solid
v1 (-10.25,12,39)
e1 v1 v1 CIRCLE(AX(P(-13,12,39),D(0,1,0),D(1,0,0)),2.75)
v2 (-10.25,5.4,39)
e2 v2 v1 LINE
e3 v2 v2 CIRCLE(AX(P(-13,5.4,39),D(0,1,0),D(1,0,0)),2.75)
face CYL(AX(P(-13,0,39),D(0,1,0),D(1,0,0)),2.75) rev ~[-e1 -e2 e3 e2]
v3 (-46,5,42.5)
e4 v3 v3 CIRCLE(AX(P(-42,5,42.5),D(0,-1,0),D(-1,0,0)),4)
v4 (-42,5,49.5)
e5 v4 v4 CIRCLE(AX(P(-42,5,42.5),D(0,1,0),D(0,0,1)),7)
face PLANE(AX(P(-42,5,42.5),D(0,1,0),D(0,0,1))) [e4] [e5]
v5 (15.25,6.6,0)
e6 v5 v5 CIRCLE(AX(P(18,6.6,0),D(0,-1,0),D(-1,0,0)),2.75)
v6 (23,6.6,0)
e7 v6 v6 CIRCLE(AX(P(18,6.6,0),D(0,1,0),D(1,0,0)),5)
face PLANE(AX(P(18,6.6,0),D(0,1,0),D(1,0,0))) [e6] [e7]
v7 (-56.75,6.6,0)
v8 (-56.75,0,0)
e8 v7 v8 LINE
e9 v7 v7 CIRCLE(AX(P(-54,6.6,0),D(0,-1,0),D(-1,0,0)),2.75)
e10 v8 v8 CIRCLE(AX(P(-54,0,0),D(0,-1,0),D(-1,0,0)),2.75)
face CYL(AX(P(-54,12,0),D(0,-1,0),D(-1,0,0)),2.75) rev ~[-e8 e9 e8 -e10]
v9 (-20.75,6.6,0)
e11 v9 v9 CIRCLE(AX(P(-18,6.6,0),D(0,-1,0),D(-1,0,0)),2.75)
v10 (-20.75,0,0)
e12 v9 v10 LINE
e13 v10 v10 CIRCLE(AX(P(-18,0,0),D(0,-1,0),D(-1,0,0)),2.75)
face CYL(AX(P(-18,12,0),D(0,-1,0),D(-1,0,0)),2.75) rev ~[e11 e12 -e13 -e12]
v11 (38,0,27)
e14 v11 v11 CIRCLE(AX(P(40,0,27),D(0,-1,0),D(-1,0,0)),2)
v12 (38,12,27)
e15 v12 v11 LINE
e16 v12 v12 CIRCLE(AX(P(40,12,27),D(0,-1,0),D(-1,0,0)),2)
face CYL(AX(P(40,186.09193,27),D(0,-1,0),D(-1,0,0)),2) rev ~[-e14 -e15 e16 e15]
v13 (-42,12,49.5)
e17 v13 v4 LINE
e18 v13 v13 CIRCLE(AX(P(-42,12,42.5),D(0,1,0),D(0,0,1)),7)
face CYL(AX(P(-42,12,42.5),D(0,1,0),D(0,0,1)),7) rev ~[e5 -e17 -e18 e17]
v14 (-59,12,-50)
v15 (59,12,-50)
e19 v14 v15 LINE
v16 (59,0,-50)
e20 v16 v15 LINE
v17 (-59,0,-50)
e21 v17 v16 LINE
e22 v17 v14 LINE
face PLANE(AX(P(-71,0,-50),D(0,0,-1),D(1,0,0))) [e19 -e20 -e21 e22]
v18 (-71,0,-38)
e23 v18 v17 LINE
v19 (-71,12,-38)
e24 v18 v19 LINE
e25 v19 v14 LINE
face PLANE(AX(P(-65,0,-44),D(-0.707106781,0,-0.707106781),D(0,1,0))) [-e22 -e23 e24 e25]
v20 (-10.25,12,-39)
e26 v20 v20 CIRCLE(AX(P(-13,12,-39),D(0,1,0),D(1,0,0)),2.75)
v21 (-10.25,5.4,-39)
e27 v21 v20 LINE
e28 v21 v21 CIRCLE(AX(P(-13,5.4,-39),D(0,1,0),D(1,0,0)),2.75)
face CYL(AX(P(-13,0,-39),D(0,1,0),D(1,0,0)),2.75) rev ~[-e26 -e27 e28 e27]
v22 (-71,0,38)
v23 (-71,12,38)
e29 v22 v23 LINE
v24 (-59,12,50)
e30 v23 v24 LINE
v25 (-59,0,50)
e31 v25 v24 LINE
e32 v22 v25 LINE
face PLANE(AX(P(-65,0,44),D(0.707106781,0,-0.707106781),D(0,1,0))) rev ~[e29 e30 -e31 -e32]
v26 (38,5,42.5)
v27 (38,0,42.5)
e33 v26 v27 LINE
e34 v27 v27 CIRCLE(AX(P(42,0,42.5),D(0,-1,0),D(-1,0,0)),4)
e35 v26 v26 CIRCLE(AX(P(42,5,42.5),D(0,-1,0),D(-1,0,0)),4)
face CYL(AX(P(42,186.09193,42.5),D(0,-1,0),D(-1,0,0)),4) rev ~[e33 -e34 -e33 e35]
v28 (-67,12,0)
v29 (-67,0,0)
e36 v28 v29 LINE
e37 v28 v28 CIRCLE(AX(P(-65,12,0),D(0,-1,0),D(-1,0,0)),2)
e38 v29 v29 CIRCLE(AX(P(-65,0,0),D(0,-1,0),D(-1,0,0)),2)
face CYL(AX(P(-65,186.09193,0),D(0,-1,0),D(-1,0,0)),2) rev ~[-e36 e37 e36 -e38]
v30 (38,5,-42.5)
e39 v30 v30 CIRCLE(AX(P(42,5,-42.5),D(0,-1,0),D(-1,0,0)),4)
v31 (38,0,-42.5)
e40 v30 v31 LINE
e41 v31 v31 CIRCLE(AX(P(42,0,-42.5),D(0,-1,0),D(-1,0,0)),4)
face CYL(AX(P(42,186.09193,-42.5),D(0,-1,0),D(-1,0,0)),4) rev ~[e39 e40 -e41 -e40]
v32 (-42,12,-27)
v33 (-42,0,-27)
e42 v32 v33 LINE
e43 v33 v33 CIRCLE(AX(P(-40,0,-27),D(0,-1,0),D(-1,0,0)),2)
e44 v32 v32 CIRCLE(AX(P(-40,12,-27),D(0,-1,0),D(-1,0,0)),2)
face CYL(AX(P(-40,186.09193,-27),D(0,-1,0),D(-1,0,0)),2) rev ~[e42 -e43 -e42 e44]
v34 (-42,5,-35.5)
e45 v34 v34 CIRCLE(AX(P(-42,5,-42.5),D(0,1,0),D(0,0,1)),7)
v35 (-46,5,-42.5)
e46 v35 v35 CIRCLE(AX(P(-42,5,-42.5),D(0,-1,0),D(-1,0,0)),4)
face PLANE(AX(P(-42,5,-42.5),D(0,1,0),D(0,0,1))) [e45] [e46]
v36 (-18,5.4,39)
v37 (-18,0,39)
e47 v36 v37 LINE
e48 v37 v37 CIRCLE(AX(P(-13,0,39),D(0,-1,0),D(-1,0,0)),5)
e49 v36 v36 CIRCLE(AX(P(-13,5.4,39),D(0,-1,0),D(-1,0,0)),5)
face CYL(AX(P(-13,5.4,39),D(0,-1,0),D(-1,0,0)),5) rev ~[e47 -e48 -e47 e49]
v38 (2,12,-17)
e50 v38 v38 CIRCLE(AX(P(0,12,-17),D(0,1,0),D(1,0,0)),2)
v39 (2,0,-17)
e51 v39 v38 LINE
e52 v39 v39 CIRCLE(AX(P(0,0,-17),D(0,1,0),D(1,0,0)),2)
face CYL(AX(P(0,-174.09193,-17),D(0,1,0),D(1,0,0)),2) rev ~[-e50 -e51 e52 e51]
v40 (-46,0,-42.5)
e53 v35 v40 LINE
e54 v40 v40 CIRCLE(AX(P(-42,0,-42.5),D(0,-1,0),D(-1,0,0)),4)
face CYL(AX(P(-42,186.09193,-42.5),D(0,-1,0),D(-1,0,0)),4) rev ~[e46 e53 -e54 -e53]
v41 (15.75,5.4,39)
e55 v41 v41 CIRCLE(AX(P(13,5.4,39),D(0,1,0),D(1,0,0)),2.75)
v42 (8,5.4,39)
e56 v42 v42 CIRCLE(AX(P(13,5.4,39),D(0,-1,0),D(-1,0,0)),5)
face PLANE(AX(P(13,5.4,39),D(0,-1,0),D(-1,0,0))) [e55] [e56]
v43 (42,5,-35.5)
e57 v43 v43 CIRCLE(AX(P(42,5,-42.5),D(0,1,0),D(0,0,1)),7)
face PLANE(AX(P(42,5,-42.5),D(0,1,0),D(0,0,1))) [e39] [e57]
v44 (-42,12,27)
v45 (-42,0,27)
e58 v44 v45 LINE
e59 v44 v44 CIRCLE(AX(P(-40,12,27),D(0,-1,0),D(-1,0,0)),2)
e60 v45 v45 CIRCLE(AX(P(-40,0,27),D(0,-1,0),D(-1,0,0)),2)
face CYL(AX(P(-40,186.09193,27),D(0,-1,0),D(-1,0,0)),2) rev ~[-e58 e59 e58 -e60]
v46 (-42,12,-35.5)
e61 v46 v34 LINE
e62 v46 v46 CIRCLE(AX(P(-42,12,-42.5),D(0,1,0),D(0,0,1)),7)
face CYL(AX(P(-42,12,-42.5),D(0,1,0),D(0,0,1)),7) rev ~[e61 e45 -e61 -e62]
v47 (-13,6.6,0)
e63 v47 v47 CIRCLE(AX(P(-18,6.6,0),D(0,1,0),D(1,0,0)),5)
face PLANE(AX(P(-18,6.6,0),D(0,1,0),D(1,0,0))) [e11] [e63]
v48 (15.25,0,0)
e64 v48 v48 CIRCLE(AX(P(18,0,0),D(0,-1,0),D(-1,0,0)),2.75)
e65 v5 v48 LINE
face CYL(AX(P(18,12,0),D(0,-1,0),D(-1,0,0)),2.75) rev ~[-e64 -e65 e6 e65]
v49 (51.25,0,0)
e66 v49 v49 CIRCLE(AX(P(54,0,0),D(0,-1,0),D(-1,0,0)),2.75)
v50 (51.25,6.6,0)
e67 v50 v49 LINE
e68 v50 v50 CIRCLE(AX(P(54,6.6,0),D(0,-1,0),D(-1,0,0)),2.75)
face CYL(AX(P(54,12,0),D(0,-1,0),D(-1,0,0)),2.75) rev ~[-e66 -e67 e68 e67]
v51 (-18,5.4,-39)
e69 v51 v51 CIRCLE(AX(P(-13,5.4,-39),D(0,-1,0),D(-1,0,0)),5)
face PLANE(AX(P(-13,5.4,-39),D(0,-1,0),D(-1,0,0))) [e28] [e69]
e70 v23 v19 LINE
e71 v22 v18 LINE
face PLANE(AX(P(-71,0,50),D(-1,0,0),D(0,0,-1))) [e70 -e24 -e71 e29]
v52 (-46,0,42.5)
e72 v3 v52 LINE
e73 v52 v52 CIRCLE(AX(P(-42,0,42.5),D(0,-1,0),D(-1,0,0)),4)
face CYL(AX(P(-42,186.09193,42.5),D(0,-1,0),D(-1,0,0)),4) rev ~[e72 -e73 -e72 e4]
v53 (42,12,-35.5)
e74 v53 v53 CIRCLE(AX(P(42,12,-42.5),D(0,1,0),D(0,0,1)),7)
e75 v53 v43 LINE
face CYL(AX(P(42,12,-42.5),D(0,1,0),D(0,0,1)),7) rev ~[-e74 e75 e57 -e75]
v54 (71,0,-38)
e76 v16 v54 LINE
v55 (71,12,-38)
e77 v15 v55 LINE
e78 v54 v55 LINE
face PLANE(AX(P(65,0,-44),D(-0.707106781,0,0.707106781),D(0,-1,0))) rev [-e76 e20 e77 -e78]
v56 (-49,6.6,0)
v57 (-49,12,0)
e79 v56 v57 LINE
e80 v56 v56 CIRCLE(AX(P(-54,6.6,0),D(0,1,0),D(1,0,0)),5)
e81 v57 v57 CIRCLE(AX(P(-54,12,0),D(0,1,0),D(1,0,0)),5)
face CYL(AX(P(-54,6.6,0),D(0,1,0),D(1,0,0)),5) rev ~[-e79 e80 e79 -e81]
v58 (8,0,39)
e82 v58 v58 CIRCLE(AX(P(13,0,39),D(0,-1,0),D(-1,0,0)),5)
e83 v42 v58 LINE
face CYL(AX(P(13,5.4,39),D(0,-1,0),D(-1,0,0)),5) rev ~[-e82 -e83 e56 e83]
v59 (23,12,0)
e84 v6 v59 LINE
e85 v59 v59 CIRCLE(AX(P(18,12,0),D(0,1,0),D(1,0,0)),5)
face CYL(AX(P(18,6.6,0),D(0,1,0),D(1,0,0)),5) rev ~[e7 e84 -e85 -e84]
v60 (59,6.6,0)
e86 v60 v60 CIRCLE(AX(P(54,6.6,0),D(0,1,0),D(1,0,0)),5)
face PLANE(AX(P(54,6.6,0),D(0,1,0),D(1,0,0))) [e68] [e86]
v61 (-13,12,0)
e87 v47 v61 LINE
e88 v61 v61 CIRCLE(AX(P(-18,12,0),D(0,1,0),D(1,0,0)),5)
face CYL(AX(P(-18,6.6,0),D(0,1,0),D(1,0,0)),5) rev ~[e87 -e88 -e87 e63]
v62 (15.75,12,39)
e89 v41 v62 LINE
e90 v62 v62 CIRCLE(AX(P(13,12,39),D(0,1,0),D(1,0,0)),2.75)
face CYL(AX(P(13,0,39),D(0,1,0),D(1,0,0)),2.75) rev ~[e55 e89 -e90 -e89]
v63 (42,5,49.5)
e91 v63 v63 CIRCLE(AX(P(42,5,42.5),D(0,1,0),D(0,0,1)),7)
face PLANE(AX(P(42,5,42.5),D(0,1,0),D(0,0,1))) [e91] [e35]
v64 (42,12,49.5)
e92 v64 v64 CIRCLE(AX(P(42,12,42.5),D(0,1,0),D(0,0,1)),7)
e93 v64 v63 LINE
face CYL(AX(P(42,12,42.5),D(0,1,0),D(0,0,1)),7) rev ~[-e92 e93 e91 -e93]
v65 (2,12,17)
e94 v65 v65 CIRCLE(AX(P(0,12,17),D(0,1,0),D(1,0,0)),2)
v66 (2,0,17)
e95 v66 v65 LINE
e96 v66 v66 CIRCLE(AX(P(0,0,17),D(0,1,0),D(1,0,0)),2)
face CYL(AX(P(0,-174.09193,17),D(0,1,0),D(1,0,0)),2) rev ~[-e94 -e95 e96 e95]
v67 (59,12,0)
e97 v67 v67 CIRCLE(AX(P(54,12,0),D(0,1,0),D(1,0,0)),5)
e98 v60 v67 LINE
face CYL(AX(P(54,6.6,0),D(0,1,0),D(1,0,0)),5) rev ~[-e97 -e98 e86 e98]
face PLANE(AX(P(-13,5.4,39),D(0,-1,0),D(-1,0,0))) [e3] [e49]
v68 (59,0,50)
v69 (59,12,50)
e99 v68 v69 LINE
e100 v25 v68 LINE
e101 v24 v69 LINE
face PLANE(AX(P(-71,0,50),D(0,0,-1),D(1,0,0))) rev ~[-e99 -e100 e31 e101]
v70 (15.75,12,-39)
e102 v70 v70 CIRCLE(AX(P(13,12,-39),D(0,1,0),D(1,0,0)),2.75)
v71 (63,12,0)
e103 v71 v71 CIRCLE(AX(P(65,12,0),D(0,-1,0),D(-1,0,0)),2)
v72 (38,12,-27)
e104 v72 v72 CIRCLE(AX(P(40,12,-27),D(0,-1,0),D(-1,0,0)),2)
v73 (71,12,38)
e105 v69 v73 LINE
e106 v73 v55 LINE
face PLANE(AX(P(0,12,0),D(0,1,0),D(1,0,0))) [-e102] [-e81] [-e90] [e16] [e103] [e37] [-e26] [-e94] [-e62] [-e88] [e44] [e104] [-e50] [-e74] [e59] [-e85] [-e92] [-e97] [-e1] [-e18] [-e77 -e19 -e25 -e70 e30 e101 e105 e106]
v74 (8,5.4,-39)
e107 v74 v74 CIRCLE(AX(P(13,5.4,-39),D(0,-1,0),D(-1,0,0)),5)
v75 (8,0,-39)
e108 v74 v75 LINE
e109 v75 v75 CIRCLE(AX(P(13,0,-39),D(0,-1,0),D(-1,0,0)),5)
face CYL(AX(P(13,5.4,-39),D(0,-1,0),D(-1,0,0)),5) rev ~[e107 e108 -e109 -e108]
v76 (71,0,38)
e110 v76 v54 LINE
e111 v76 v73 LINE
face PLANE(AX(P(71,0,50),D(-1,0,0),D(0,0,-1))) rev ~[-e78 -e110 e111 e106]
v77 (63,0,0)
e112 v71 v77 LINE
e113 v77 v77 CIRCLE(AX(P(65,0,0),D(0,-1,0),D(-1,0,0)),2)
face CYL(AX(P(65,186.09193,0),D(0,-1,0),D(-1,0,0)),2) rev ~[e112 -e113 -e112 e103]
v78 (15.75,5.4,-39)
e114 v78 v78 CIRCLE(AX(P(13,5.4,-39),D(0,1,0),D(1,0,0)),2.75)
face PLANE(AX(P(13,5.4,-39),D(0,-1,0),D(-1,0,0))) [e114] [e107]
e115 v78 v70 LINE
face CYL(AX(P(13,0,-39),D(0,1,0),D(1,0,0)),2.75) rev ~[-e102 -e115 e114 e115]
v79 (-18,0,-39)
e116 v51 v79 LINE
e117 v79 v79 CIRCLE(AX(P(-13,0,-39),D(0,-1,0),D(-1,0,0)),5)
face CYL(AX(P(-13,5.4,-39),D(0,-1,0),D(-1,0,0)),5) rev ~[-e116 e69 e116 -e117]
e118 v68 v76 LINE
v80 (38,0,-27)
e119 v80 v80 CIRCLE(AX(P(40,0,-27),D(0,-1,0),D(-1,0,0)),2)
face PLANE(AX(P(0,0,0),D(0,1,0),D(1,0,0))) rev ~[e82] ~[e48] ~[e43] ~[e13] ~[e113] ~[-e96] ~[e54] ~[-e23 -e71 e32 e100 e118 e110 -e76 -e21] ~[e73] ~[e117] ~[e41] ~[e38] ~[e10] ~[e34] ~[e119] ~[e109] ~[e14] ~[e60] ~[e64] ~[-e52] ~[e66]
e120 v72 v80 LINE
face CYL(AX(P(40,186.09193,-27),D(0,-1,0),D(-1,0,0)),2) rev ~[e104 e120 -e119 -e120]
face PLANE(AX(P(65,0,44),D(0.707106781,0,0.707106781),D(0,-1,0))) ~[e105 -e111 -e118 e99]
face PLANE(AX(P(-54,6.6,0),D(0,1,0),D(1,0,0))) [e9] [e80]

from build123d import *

# Parameters (mm, degrees)
SKETCH1_W                                           = 142
SKETCH1_H                                           = 100
EXTRUDE1_DEPTH                                      = 12
CBORE_FOR_M5_HEX_SOCKET_HEAD_CAP_SCREW1_D           = 5.5
CBORE_FOR_M5_HEX_SOCKET_HEAD_CAP_SCREW1_CBORE_D     = 10
CBORE_FOR_M5_HEX_SOCKET_HEAD_CAP_SCREW1_CBORE_DEPTH = 5.4
CBORE_FOR_M5_HEX_SOCKET_HEAD_CAP_SCREW2_D           = 5.5
CBORE_FOR_M5_HEX_SOCKET_HEAD_CAP_SCREW2_CBORE_D     = 10
CBORE_FOR_M5_HEX_SOCKET_HEAD_CAP_SCREW2_CBORE_DEPTH = 5.4
MM_0_D                                              = 4
CHAMFER1_SIZE                                       = 12
F_4_0_MM_DOWEL_HOLES1_D                             = 4
F_8_0_MM_DOWEL_HOLES1_D                             = 8
SKETCH13_R                                          = 7
EXTRUDE2_DEPTH                                      = 7
F_4_0_MM_DOWEL_HOLES2_D                             = 4


with BuildPart() as part:
    # Sketch1 → Extrude1 (new body)
    with BuildSketch(Plane(origin=(0, 0, 0), x_dir=(1, 0, 0), z_dir=(0, 1, 0))):
        Rectangle(SKETCH1_W, SKETCH1_H)
    extrude(amount=EXTRUDE1_DEPTH)

    # CBORE for M5 Hex Socket Head Cap Screw1 (through all)
    with Locations(Plane(origin=(0, 0, 0), x_dir=(-1, 0, 0), z_dir=(0, -1, 0))):
        with Locations((-13, -39), (13, 39), (-13, 39), (13, -39)):
            CounterBoreHole(CBORE_FOR_M5_HEX_SOCKET_HEAD_CAP_SCREW1_D / 2, CBORE_FOR_M5_HEX_SOCKET_HEAD_CAP_SCREW1_CBORE_D / 2, CBORE_FOR_M5_HEX_SOCKET_HEAD_CAP_SCREW1_CBORE_DEPTH)

    # CBORE for M5 Hex Socket Head Cap Screw2 (through all)
    with Locations(Plane(origin=(0, 12, 0), x_dir=(1, 0, 0), z_dir=(0, 1, 0))):
        with Locations((-54, 0), (54, 0), (-18, 0), (18, 0)):
            CounterBoreHole(CBORE_FOR_M5_HEX_SOCKET_HEAD_CAP_SCREW2_D / 2, CBORE_FOR_M5_HEX_SOCKET_HEAD_CAP_SCREW2_CBORE_D / 2, CBORE_FOR_M5_HEX_SOCKET_HEAD_CAP_SCREW2_CBORE_DEPTH)

    # 大小mm 暗销孔0 (through all)
    with Locations(Plane(origin=(0, 12, 0), x_dir=(1, 0, 0), z_dir=(0, 1, 0))):
        with Locations((-40, 27), (40, 27), (40, -27), (-40, -27)):
            Hole(MM_0_D / 2)

    # Chamfer1
    chamfer1_edges = [part.edges().sort_by_distance(p)[0] for p in [
        (-71, 6, -50),
        (71, 6, -50),
        (71, 6, 50),
        (-71, 6, 50),
    ]]
    chamfer(chamfer1_edges, length=CHAMFER1_SIZE)

    # Ø4.0 mm Dowel Holes1 (through all)
    with Locations(Plane(origin=(0, 12, 0), x_dir=(1, 0, 0), z_dir=(0, 1, 0))):
        with Locations((-65, 0), (65, 0)):
            Hole(F_4_0_MM_DOWEL_HOLES1_D / 2)

    # Ø8.0 mm Dowel Holes1 (through all)
    with Locations(Plane(origin=(0, 12, 0), x_dir=(1, 0, 0), z_dir=(0, 1, 0))):
        with Locations((-42, 42.5), (42, 42.5), (42, -42.5), (-42, -42.5)):
            Hole(F_8_0_MM_DOWEL_HOLES1_D / 2)

    # Sketch13 → Extrude2 (cut)
    with BuildSketch(Plane(origin=(0, 12, 0), x_dir=(1, 0, 0), z_dir=(0, 1, 0))):
        with Locations(Location((-42, -42.5, 0), (0, 0, 270))):
            Circle(SKETCH13_R)
        with Locations(Location((42, -42.5, 0), (0, 0, 270))):
            Circle(SKETCH13_R)
        with Locations(Location((-42, 42.5, 0), (0, 0, 270))):
            Circle(SKETCH13_R)
        with Locations(Location((42, 42.5, 0), (0, 0, 270))):
            Circle(SKETCH13_R)
    extrude(amount=-EXTRUDE2_DEPTH, mode=Mode.SUBTRACT)

    # Ø4.0 mm Dowel Holes2 (through all)
    with Locations(Plane(origin=(0, 0, 0), x_dir=(-1, 0, 0), z_dir=(0, -1, 0))):
        with Locations((0, 17), (0, -17)):
            Hole(F_4_0_MM_DOWEL_HOLES2_D / 2)


solid = part.part
